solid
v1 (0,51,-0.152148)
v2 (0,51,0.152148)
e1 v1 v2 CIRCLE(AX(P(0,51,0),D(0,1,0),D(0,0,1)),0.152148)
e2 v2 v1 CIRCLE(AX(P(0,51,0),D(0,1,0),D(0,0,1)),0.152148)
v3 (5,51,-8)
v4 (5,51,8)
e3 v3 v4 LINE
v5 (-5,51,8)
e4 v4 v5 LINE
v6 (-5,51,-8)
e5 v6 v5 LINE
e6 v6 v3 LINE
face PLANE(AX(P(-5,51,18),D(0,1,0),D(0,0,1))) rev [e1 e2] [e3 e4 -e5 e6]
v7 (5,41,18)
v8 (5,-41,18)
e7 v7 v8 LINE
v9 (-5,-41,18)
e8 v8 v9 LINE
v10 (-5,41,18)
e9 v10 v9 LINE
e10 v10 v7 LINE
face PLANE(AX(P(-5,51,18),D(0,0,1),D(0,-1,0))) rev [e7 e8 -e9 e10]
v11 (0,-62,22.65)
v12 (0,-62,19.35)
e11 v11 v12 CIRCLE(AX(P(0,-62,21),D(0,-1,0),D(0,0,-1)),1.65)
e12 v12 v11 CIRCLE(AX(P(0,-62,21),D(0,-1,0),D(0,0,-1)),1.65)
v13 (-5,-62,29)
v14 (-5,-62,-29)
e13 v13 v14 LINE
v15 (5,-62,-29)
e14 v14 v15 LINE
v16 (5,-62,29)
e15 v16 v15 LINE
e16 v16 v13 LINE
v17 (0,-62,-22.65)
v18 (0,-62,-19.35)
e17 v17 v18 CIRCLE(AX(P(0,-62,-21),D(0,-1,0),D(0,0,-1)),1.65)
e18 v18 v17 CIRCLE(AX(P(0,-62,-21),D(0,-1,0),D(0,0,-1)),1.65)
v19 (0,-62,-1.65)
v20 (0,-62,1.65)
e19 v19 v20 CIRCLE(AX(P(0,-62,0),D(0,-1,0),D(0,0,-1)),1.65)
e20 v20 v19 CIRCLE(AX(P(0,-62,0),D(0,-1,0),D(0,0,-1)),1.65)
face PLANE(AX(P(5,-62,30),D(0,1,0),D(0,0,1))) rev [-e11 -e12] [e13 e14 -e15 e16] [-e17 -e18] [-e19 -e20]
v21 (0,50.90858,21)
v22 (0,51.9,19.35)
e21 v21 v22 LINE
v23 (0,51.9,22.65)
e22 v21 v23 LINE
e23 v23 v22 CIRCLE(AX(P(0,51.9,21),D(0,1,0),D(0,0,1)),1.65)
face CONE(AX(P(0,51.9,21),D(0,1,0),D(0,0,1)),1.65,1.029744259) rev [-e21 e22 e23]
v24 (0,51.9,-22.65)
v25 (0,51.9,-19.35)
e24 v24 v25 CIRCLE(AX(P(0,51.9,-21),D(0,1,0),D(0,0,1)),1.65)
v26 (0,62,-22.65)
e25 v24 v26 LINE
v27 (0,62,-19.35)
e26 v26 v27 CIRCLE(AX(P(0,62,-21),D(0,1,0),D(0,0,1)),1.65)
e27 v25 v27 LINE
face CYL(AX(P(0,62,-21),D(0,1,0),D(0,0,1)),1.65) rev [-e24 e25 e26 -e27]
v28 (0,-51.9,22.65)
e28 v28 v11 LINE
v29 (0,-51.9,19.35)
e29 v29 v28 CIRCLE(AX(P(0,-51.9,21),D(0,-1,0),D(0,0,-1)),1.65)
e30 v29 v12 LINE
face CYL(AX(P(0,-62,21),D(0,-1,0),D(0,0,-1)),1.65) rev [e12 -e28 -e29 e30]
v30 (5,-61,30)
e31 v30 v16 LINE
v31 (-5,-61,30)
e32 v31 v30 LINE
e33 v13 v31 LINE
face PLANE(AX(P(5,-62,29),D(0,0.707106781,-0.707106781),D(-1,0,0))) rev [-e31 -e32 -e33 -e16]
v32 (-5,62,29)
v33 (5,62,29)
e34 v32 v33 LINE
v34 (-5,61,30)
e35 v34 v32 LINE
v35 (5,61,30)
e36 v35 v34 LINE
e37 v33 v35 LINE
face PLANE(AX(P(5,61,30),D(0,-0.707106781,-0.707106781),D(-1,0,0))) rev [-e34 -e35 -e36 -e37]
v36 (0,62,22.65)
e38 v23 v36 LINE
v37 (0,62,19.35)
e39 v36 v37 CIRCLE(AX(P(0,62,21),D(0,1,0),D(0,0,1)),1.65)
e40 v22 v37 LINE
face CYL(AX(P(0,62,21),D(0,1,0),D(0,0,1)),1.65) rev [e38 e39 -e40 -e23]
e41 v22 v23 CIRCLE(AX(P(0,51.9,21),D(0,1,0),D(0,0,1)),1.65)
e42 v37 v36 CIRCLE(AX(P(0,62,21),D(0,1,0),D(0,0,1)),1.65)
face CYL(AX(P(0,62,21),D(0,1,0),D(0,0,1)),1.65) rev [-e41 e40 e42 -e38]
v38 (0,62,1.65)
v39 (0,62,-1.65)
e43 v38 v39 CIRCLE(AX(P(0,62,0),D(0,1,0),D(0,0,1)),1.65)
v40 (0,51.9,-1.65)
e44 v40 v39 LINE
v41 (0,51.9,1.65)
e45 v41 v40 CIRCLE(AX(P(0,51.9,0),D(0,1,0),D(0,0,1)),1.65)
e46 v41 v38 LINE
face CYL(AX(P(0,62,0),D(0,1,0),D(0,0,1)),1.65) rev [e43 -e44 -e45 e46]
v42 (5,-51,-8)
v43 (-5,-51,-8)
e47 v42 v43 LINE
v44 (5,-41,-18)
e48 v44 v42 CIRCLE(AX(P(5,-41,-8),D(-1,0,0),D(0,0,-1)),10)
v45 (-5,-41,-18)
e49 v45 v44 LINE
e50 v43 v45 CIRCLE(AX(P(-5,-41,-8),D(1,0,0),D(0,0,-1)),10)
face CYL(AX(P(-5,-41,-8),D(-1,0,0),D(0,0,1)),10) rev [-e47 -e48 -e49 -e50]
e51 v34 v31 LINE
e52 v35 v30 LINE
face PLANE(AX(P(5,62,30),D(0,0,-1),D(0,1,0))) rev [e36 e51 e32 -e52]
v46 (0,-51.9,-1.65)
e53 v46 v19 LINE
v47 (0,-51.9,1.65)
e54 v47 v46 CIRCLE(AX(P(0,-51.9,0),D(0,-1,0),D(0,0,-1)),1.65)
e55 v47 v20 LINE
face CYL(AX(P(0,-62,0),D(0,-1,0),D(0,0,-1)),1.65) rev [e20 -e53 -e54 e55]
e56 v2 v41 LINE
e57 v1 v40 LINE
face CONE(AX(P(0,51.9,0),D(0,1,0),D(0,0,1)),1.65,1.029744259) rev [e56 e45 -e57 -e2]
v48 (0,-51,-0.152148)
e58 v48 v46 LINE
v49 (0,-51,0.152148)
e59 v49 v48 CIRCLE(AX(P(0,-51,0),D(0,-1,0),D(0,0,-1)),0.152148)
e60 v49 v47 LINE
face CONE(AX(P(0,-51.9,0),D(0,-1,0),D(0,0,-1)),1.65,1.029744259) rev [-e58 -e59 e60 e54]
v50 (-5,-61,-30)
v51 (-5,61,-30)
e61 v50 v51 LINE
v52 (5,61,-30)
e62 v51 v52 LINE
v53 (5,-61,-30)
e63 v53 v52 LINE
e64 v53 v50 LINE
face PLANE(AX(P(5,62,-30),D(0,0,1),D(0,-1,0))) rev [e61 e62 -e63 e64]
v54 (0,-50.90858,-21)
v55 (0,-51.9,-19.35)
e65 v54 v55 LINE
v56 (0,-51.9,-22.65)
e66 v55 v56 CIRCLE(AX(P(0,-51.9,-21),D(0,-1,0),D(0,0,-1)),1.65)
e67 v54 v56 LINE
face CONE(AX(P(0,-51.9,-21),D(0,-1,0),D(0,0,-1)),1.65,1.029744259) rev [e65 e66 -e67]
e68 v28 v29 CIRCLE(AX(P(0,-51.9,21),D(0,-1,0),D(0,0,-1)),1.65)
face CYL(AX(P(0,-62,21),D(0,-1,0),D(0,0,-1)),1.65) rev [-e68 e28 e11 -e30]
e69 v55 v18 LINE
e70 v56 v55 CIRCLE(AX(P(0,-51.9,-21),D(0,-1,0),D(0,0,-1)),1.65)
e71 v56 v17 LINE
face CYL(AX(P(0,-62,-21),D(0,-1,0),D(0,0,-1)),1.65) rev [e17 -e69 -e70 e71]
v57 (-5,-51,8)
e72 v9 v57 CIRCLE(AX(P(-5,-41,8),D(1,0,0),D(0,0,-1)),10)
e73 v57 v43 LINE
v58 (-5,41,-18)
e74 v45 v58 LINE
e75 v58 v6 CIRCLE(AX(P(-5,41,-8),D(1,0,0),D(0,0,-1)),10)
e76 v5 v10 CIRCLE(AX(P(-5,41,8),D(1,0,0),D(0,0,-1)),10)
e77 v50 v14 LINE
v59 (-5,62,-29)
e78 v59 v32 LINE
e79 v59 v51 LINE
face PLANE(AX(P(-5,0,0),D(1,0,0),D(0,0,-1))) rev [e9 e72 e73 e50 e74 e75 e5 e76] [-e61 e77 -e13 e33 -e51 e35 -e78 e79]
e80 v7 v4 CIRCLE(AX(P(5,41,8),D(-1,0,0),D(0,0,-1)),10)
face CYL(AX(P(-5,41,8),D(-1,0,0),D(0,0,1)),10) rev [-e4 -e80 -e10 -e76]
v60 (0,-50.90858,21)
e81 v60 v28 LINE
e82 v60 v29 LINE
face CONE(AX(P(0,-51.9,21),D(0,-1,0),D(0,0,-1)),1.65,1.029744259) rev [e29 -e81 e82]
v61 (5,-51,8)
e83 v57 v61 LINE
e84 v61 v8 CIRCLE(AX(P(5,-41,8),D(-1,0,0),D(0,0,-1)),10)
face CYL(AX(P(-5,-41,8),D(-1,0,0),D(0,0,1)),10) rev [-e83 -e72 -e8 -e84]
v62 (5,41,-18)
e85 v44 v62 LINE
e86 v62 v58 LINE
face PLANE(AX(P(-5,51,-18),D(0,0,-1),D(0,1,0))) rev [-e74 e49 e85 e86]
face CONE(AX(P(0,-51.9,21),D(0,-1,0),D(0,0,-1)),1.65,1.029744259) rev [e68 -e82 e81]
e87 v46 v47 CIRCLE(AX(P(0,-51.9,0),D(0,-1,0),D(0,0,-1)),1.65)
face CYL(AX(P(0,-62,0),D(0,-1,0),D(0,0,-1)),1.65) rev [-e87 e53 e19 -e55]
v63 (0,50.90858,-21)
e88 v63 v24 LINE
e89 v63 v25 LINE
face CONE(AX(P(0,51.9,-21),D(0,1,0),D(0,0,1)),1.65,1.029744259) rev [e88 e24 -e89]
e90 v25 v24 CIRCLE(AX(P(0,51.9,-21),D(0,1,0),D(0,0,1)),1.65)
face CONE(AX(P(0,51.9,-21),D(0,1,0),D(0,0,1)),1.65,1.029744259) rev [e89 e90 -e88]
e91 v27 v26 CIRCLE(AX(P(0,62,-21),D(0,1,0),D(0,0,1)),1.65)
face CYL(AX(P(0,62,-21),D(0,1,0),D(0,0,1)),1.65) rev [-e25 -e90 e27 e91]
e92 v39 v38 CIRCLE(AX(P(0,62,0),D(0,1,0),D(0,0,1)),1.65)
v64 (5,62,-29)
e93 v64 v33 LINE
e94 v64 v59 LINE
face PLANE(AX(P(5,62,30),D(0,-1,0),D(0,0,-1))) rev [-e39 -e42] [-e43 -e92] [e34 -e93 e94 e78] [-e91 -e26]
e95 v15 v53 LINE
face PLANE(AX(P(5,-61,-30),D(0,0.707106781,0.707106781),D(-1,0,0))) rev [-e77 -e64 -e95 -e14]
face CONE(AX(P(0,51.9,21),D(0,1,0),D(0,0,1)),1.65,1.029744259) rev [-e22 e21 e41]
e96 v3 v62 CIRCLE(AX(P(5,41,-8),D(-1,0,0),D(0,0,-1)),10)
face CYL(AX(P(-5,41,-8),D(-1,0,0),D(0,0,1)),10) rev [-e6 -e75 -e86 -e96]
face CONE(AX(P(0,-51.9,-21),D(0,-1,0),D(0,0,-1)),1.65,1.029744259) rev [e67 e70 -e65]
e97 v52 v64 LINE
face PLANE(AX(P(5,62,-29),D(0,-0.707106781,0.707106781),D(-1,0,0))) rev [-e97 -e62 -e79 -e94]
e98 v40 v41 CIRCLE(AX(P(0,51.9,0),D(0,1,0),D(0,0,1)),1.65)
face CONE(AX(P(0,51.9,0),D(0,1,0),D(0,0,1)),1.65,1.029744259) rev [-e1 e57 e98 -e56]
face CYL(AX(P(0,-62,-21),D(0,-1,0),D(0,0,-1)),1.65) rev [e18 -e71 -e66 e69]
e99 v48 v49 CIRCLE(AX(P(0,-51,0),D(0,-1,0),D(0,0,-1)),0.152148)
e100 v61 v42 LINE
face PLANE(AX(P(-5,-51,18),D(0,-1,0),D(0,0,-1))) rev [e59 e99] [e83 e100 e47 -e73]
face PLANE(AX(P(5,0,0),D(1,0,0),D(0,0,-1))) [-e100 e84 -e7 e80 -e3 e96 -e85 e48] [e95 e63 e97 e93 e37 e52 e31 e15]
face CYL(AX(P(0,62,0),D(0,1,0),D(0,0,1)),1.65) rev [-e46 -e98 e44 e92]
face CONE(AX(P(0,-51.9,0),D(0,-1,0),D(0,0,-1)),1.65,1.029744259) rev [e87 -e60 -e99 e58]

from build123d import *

# Parameters (mm, degrees)
SKETCH1_W             = 60
SKETCH1_H             = 124
BOSS_EXTRUDE1_DEPTH   = 5
SKETCH2_W             = 36
SKETCH2_H             = 102
CUT_EXTRUDE1_DEPTH    = 70.598850565
M4_TAPPED_HOLE1_D     = 3.3
M4_TAPPED_HOLE1_DEPTH = 10.1
M4_TAPPED_HOLE1_TIP   = 0.991420021
FILLET1_R             = 10
M4_TAPPED_HOLE2_D     = 3.3
M4_TAPPED_HOLE2_DEPTH = 10.1
M4_TAPPED_HOLE2_TIP   = 0.991420021
CHAMFER1_SIZE         = 1


with BuildPart() as part:
    # Sketch1 → Boss-Extrude1 (new, symmetric)
    with BuildSketch(Plane(origin=(0, 0, 0), x_dir=(0, 0, -1), z_dir=(1, 0, 0))):
        Rectangle(SKETCH1_W, SKETCH1_H)
    extrude(amount=BOSS_EXTRUDE1_DEPTH, both=True)

    # Sketch2 → Cut-Extrude1 (cut, through all)
    with BuildSketch(Plane(origin=(5, 0, 0), x_dir=(0, 0, -1), z_dir=(1, 0, 0))):
        Rectangle(SKETCH2_W, SKETCH2_H)
    extrude(amount=-CUT_EXTRUDE1_DEPTH, mode=Mode.SUBTRACT)

    # M4 Tapped Hole1
    with Locations(Plane(origin=(0, 62, 0), x_dir=(1, 0, 0), z_dir=(0, 1, 0))):
        with Locations((0, 0), (0, 21), (0, -21)):
            Hole(M4_TAPPED_HOLE1_D / 2, depth=M4_TAPPED_HOLE1_DEPTH)
            with Locations((0, 0, -(M4_TAPPED_HOLE1_DEPTH + M4_TAPPED_HOLE1_TIP / 2))):  # 118° drill point
                Cone(0, M4_TAPPED_HOLE1_D / 2, M4_TAPPED_HOLE1_TIP, mode=Mode.SUBTRACT)

    # Fillet1
    fillet1_edges = [part.edges().sort_by_distance(p)[0] for p in [
        (0, 51, -18),
        (0, -51, -18),
        (0, -51, 18),
        (0, 51, 18),
    ]]
    fillet(fillet1_edges, radius=FILLET1_R)

    # M4 Tapped Hole2
    with Locations(Plane(origin=(0, -62, 0), x_dir=(-1, 0, 0), z_dir=(0, -1, 0))):
        with Locations((0, 0), (0, 21), (0, -21)):
            Hole(M4_TAPPED_HOLE2_D / 2, depth=M4_TAPPED_HOLE2_DEPTH)
            with Locations((0, 0, -(M4_TAPPED_HOLE2_DEPTH + M4_TAPPED_HOLE2_TIP / 2))):  # 118° drill point
                Cone(0, M4_TAPPED_HOLE2_D / 2, M4_TAPPED_HOLE2_TIP, mode=Mode.SUBTRACT)

    # Chamfer1
    chamfer1_edges = [part.edges().sort_by_distance(p)[0] for p in [
        (0, -62, -30),
        (0, -62, 30),
        (0, 62, 30),
        (0, 62, -30),
    ]]
    chamfer(chamfer1_edges, length=CHAMFER1_SIZE)


solid = part.part
